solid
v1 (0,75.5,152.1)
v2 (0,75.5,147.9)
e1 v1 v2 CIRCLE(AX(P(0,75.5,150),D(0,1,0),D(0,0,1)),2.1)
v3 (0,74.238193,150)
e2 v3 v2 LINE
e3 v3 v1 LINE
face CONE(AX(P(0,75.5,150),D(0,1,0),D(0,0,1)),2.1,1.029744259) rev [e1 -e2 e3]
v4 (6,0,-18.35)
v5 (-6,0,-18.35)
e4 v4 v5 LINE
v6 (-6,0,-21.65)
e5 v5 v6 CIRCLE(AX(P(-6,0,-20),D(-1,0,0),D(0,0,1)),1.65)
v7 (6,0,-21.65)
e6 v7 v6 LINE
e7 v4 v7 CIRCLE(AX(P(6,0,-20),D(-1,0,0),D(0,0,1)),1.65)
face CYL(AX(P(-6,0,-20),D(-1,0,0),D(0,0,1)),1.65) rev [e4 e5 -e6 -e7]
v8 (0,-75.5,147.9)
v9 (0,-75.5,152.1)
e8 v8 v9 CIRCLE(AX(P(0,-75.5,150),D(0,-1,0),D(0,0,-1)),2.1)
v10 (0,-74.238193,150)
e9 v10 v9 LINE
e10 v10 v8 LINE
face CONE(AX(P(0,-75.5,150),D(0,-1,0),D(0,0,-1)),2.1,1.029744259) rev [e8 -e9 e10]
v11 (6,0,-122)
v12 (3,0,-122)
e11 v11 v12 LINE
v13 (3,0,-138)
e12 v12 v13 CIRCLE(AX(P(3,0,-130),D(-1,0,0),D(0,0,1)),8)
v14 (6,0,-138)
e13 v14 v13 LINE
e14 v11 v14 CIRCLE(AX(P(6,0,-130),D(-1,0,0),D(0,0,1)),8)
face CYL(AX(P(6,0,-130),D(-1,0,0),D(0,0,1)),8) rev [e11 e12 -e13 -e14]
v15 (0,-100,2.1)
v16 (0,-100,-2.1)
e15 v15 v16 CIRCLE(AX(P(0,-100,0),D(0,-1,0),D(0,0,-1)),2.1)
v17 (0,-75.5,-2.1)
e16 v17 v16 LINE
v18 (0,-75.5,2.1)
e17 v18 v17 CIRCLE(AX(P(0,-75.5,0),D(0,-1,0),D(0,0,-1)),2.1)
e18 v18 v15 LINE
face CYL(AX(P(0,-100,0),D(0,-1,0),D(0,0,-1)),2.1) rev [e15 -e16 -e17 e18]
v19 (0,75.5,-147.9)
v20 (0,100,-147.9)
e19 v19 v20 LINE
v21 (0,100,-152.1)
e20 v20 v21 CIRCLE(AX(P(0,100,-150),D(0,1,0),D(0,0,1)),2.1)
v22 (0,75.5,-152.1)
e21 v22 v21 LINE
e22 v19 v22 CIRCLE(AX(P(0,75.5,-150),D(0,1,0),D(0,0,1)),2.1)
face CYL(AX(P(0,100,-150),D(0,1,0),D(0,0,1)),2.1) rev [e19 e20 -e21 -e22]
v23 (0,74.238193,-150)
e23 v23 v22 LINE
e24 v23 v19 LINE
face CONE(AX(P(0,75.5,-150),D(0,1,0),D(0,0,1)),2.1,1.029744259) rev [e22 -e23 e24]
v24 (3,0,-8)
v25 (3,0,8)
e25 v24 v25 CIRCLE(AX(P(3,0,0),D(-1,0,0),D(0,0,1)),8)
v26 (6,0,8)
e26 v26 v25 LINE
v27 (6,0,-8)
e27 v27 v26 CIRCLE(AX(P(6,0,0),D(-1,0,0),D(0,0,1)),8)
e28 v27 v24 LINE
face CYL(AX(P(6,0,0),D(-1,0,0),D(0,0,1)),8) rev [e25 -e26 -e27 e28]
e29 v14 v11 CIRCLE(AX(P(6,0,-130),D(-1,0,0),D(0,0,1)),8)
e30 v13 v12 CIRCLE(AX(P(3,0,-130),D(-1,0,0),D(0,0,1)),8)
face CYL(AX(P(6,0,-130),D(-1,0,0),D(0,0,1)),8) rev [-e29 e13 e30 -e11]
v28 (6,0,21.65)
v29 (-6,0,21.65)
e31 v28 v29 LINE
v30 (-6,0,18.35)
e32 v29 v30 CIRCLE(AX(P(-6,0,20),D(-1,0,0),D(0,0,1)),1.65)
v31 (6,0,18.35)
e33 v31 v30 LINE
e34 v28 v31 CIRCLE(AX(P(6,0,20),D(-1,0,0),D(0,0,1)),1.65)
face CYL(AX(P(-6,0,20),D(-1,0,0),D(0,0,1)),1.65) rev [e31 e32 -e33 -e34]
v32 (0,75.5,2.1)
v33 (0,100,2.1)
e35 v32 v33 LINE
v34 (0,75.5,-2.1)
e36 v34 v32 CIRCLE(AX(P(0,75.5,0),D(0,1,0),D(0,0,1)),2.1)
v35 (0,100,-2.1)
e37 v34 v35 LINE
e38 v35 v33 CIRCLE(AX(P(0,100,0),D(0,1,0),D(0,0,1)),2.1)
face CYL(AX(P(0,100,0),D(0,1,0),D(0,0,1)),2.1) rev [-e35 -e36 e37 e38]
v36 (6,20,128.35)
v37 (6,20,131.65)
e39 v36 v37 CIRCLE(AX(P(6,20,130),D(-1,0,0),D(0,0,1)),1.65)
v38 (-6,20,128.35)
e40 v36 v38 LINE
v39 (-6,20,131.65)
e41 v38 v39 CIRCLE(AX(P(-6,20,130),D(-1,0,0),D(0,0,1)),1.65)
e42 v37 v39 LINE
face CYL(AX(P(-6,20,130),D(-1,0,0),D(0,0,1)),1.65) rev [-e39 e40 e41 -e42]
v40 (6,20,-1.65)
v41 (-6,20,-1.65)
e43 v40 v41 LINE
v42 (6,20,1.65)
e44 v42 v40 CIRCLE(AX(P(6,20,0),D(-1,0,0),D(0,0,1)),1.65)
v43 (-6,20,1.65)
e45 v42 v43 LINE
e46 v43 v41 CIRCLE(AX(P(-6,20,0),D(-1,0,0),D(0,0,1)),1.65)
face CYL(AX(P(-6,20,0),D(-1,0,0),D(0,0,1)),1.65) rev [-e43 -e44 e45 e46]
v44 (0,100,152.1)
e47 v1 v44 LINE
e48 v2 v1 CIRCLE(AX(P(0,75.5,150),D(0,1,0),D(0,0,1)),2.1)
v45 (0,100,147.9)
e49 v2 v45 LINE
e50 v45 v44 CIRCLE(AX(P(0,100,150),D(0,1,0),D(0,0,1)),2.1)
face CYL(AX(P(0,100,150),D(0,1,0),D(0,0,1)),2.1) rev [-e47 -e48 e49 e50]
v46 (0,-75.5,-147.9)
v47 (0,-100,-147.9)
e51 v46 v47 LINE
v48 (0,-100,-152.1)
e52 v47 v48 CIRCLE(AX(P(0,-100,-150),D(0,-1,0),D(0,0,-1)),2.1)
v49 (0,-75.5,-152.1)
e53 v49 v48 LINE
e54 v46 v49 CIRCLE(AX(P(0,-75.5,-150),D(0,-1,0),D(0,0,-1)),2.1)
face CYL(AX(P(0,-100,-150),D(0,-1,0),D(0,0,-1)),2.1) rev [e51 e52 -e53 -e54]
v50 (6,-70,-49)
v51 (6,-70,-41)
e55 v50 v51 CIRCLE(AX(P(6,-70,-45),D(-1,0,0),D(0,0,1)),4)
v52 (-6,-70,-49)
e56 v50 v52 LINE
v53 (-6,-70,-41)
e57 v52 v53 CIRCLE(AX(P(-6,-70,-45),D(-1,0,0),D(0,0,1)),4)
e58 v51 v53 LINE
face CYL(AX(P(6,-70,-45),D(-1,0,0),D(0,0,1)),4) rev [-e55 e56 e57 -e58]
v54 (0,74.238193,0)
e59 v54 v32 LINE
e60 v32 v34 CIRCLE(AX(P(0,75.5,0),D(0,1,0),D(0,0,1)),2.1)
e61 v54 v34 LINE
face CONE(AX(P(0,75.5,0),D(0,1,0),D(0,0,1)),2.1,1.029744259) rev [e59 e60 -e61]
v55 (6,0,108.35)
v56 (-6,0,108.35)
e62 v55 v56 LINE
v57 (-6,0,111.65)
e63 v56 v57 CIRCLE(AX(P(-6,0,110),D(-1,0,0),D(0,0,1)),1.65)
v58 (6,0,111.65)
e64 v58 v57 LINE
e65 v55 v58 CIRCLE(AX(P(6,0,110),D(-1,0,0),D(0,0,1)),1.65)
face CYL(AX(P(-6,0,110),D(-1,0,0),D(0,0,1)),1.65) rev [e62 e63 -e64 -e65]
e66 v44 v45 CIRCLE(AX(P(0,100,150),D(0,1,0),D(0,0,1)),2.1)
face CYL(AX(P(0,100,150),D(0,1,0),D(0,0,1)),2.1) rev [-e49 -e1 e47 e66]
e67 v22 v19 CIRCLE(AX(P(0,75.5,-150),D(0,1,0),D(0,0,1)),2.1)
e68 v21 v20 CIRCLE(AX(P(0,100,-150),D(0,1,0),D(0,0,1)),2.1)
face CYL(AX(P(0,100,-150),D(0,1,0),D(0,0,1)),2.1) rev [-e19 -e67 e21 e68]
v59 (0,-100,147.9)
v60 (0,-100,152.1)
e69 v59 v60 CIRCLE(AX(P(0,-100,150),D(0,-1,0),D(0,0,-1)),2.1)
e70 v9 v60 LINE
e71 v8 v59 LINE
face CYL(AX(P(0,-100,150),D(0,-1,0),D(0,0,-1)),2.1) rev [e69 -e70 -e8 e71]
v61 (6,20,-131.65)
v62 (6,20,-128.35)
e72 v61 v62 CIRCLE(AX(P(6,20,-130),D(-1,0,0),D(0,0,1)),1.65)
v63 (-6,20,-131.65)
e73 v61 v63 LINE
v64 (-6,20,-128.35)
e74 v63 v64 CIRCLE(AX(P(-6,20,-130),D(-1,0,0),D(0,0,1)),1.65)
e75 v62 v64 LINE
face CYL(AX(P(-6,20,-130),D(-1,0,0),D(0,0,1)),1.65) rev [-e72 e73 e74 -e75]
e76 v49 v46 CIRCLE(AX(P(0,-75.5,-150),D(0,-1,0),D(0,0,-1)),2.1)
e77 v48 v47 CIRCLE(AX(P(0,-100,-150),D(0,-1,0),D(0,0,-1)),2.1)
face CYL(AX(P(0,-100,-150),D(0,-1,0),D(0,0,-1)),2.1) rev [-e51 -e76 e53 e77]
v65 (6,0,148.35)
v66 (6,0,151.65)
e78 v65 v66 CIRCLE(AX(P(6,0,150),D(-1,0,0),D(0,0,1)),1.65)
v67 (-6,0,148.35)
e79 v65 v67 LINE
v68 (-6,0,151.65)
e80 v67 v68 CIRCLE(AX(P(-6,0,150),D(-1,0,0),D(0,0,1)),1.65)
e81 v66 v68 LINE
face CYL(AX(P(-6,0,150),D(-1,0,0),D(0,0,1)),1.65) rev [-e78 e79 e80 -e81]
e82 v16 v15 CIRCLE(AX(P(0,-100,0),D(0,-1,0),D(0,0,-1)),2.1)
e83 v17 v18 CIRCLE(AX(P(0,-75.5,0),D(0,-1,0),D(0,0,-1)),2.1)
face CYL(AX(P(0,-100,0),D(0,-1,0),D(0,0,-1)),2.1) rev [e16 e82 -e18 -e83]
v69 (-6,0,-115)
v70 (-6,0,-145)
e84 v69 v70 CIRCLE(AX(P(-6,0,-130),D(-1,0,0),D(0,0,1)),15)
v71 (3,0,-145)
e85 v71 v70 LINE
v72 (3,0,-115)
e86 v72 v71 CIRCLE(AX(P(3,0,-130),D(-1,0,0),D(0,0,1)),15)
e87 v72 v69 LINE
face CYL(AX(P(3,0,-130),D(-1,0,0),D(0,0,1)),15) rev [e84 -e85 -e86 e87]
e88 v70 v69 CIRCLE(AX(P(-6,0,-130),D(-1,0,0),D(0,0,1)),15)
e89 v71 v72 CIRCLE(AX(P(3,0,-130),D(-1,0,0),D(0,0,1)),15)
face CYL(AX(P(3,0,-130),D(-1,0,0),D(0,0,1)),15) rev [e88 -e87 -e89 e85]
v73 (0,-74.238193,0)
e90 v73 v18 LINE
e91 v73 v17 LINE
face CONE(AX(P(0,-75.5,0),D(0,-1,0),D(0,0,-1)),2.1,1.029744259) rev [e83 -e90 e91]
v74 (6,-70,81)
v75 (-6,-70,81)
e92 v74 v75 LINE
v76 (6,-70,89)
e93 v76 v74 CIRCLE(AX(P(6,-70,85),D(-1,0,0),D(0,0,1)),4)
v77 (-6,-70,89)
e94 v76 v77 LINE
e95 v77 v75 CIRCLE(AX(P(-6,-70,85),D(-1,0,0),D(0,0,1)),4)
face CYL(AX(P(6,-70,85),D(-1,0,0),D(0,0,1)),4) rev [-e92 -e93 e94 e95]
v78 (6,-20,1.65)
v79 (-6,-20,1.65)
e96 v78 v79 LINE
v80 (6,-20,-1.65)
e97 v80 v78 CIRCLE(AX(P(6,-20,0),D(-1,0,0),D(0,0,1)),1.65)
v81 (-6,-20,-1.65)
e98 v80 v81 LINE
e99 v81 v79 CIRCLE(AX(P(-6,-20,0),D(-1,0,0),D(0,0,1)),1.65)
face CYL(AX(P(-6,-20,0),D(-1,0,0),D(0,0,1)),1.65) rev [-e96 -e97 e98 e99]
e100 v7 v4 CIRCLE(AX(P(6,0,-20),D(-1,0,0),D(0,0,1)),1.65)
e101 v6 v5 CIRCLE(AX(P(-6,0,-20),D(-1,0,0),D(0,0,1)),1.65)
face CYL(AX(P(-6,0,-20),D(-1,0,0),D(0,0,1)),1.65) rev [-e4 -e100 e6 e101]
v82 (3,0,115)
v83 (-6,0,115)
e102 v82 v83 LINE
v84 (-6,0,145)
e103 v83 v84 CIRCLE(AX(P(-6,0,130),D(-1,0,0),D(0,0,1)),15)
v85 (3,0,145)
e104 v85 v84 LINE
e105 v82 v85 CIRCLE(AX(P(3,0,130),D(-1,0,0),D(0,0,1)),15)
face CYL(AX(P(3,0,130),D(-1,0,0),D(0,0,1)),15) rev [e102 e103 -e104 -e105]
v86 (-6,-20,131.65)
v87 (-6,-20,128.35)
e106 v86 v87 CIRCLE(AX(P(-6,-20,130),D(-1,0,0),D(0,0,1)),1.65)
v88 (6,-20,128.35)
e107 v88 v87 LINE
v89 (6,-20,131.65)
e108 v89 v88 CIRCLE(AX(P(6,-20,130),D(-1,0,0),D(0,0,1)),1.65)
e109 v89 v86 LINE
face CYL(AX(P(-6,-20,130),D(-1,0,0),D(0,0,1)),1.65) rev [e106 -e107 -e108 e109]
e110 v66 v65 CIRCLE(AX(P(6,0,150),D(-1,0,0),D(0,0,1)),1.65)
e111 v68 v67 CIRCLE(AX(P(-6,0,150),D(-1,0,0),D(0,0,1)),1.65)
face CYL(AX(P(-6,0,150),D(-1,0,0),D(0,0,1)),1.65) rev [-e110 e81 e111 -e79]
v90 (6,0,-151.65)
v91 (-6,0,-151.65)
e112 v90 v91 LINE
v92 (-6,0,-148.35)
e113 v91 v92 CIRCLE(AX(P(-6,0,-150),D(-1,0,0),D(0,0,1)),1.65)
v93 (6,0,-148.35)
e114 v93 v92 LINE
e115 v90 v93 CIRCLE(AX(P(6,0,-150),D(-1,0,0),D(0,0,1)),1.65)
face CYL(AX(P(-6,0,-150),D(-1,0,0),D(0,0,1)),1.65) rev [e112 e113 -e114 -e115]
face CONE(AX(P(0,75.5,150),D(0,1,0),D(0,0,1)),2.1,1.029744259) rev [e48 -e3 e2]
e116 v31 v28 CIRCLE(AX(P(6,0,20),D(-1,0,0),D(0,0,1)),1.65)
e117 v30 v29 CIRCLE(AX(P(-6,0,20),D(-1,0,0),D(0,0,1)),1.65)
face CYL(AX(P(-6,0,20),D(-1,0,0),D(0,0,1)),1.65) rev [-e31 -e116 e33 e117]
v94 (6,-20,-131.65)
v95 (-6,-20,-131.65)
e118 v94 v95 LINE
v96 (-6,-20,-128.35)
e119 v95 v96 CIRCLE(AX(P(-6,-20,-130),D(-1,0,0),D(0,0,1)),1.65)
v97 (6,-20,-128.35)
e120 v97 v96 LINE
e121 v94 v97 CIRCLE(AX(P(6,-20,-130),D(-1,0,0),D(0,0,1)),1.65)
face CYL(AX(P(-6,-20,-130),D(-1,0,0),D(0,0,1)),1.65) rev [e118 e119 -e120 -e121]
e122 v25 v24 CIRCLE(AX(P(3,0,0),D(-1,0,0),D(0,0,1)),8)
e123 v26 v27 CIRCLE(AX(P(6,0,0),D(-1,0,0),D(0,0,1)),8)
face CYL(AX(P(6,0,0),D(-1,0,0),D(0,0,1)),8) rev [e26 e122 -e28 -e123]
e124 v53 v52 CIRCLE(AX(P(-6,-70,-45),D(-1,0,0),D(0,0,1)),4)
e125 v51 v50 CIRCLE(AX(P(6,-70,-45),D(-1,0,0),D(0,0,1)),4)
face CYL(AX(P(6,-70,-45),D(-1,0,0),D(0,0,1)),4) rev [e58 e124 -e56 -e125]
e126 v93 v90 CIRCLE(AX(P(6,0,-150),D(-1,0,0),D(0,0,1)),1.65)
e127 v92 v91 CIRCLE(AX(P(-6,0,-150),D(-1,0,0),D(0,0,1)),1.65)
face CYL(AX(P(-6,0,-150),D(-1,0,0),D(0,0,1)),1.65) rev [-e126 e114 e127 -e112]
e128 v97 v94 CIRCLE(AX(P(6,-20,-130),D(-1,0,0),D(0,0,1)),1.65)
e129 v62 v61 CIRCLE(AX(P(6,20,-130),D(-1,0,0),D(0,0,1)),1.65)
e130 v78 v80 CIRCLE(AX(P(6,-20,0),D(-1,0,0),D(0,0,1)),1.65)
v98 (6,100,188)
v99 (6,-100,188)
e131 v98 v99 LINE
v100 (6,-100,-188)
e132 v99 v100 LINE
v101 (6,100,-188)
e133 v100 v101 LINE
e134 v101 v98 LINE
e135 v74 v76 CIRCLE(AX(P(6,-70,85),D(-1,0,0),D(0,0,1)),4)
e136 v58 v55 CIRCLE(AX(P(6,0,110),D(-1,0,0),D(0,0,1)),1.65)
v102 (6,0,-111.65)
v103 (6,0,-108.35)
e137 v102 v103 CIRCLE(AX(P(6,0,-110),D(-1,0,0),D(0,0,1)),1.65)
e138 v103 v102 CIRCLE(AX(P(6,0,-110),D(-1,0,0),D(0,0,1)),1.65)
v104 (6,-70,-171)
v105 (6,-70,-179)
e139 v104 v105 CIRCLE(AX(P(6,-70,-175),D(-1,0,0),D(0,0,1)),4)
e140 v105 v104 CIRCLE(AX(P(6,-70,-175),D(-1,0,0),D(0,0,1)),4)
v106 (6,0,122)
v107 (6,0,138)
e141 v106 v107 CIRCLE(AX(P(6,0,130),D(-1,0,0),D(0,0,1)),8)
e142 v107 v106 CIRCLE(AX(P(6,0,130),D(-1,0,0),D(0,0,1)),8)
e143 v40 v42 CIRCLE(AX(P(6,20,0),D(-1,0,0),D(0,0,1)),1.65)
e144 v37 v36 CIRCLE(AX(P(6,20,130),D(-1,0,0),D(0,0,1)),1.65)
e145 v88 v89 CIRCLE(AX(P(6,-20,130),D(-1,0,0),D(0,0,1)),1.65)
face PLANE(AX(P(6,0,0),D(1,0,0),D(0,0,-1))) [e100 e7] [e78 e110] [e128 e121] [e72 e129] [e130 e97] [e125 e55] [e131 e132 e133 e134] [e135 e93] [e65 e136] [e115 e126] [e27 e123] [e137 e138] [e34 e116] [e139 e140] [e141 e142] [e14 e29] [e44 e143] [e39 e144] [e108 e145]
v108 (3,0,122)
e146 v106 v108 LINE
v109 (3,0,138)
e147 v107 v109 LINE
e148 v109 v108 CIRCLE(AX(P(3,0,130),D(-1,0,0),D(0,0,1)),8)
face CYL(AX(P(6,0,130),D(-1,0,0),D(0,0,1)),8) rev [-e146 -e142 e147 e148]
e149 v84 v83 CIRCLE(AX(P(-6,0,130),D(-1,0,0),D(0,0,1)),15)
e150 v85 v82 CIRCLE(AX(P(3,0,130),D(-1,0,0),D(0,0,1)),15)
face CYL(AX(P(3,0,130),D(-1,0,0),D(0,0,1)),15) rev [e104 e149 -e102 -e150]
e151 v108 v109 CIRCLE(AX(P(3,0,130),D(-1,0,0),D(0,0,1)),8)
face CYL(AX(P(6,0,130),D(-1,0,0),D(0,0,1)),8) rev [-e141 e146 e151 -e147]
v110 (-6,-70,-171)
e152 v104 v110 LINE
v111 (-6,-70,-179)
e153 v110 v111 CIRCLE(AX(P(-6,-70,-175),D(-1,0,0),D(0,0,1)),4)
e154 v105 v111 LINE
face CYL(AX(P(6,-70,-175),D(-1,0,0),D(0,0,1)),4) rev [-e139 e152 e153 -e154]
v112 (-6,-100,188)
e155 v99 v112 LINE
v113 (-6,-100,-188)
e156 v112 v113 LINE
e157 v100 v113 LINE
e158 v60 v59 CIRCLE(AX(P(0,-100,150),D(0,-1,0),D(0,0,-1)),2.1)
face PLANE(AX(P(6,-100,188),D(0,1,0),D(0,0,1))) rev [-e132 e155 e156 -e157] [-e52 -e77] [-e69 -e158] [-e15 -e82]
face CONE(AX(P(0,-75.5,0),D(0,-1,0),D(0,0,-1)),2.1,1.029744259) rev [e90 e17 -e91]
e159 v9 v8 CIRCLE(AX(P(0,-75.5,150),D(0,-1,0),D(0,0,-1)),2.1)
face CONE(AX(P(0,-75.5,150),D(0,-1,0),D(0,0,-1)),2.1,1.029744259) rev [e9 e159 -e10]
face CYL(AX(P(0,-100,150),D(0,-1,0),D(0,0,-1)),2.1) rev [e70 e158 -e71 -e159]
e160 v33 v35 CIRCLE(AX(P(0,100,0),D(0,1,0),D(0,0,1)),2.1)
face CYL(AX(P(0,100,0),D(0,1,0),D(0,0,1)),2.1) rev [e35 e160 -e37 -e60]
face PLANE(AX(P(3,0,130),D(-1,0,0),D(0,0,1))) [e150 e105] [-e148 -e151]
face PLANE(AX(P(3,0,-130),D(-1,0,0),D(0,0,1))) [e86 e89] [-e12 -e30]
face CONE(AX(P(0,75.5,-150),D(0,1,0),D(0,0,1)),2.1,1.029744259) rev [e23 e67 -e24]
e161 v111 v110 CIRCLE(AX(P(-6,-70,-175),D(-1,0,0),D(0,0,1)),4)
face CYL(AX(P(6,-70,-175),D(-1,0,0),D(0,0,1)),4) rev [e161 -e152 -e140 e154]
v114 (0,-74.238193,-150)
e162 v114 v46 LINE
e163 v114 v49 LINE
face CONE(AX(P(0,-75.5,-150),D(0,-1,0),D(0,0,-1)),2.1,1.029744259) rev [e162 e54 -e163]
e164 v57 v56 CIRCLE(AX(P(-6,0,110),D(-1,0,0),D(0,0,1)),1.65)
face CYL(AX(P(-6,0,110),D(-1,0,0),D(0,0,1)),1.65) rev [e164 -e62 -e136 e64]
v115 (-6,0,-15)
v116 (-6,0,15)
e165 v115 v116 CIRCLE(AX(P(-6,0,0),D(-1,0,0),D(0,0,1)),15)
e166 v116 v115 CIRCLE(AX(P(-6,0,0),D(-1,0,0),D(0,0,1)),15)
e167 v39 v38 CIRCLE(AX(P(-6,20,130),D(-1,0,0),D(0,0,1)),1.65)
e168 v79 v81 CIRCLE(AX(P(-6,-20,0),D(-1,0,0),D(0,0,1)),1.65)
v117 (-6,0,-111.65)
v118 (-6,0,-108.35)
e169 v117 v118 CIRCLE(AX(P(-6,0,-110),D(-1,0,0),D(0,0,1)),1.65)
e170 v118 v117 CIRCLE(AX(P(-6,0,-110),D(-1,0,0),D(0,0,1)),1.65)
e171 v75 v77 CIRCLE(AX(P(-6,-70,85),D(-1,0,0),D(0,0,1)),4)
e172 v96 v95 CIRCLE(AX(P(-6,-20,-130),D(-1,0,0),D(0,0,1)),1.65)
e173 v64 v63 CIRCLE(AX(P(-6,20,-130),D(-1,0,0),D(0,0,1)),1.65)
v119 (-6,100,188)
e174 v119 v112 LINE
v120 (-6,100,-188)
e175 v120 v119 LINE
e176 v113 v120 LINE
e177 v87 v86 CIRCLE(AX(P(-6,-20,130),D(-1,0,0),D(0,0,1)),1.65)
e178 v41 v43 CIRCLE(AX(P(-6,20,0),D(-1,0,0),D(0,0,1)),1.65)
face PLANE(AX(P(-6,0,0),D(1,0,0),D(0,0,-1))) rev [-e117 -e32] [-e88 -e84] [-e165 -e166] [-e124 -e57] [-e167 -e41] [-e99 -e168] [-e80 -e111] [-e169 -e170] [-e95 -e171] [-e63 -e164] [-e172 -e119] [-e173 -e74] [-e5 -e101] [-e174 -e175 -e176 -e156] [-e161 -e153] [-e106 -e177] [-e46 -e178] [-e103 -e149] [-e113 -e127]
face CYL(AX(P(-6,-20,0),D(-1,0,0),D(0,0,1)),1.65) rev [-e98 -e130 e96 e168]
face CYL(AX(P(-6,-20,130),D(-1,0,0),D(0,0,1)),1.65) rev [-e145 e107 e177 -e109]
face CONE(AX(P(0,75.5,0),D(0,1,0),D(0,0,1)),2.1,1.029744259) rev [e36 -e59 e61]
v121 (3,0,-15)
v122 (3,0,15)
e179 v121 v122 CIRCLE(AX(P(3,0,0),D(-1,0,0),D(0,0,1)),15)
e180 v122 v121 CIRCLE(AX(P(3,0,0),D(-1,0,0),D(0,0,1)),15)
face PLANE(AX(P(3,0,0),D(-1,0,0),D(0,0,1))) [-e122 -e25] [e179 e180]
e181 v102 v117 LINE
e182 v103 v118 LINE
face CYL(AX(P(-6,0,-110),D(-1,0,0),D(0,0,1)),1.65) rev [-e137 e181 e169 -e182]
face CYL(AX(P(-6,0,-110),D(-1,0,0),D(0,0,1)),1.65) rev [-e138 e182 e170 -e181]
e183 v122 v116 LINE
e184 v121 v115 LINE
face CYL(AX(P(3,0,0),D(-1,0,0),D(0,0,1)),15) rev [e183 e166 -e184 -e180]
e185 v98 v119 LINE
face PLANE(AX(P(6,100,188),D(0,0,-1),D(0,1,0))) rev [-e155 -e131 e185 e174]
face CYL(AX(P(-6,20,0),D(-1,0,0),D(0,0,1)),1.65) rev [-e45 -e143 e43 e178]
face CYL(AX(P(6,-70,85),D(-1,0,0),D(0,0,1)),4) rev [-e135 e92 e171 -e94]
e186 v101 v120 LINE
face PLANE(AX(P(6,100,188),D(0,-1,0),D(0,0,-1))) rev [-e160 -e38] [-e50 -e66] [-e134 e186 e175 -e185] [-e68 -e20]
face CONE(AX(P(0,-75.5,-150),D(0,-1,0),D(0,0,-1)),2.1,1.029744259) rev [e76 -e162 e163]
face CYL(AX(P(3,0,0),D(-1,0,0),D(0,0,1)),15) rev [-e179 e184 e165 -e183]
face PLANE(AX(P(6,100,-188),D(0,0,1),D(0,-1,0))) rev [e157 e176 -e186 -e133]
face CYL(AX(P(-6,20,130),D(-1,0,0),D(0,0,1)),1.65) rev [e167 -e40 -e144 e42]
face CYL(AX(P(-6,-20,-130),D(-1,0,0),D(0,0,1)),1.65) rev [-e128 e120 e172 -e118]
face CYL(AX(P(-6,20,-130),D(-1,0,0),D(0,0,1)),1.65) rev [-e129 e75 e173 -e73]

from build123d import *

# Parameters (mm, degrees)
SKETCH1_W                  = 376
SKETCH1_H                  = 200
BOSS_EXTRUDE1_DEPTH        = 6
M5_TAPPED_HOLE1_AT_2_COUNT = 2
M5_TAPPED_HOLE1_AT_2_PITCH = 300
M5_TAPPED_HOLE1_AT_3_COUNT = 2
M5_TAPPED_HOLE1_AT_3_PITCH = 150
SKETCH4_R                  = 15
CUT_EXTRUDE1_DEPTH         = 9
SKETCH6_R                  = 8
CUT_EXTRUDE2_DEPTH         = 214.279159788
M4_TAPPED_HOLE1_D          = 3.3
SKETCH9_R                  = 4
CUT_EXTRUDE3_DEPTH         = 214.279159788


with BuildPart() as part:
    # Sketch1 → Boss-Extrude1 (new, symmetric)
    with BuildSketch(Plane(origin=(0, 0, 0), x_dir=(0, 0, -1), z_dir=(1, 0, 0))):
        Rectangle(SKETCH1_W, SKETCH1_H)
    extrude(amount=BOSS_EXTRUDE1_DEPTH, both=True)

    # Sketch3 → M5 Tapped Hole1 (revolve, cut)
    with BuildSketch(Plane(origin=(0, 100, -150), x_dir=(0, 0, 1), z_dir=(1, 0, 0))):
        Polygon((0, 0), (0, 25.7618073), (2.1, 24.5), (2.1, 0), align=None)
    m5_tapped_hole1 = revolve(axis=Axis((0, 106.35, -150), (0, -1, 0)), mode=Mode.SUBTRACT)

    # M5 Tapped Hole1 at 2: M5 Tapped Hole1 ×2
    with Locations(*[(0, 0, i * M5_TAPPED_HOLE1_AT_2_PITCH) for i in range(1, M5_TAPPED_HOLE1_AT_2_COUNT)]):
        add(m5_tapped_hole1, mode=Mode.SUBTRACT)

    # M5 Tapped Hole1 at 3: M5 Tapped Hole1 ×2
    with Locations(*[(0, 0, i * M5_TAPPED_HOLE1_AT_3_PITCH) for i in range(1, M5_TAPPED_HOLE1_AT_3_COUNT)]):
        add(m5_tapped_hole1, mode=Mode.SUBTRACT)

    # Mirror1: M5 Tapped Hole1 across plane
    add(m5_tapped_hole1.mirror(Plane.ZX), mode=Mode.SUBTRACT)

    # Mirror1 copy 1 sketch → Mirror1 copy 1 (revolve, cut)
    with BuildSketch(Plane(origin=(0, -100, 150), x_dir=(0, 0, 1), z_dir=(1, 0, 0))):
        Polygon((0, 0), (0, -25.7618073), (2.1, -24.5), (2.1, 0), align=None)
    revolve(axis=Axis((0, -106.35, 150), (0, -1, 0)), mode=Mode.SUBTRACT)

    # Mirror1 copy 2 sketch → Mirror1 copy 2 (revolve, cut)
    with BuildSketch(Plane(origin=(0, -100, 0), x_dir=(0, 0, 1), z_dir=(1, 0, 0))):
        Polygon((0, 0), (0, -25.7618073), (2.1, -24.5), (2.1, 0), align=None)
    revolve(axis=Axis((0, -106.35, 0), (0, -1, 0)), mode=Mode.SUBTRACT)

    # Sketch4 → Cut-Extrude1 (cut)
    with BuildSketch(Plane.ZY.offset(6)):
        with Locations((-130, 0)):
            Circle(SKETCH4_R)
        Circle(SKETCH4_R)
        with Locations((130, 0)):
            Circle(SKETCH4_R)
    extrude(amount=-CUT_EXTRUDE1_DEPTH, mode=Mode.SUBTRACT)

    # Sketch6 → Cut-Extrude2 (cut, through all)
    with BuildSketch(Plane.ZY.offset(6)):
        with Locations((-130, 0)):
            Circle(SKETCH6_R)
        Circle(SKETCH6_R)
        with Locations((130, 0)):
            Circle(SKETCH6_R)
    extrude(amount=-CUT_EXTRUDE2_DEPTH, mode=Mode.SUBTRACT)

    # M4 Tapped Hole1 (through all)
    with Locations(Plane.ZY.offset(6)):
        with Locations((130, -20), (-150, 0), (-130, 20), (-110, 0), (-130, -20), (-20, 0), (0, 20), (20, 0), (0, -20), (110, 0), (130, 20), (150, 0)):
            Hole(M4_TAPPED_HOLE1_D / 2)

    # Sketch9 → Cut-Extrude3 (cut, through all)
    with BuildSketch(Plane.ZY.offset(6)):
        with Locations((-175, -70)):
            Circle(SKETCH9_R)
        with Locations((-45, -70)):
            Circle(SKETCH9_R)
        with Locations((85, -70)):
            Circle(SKETCH9_R)
    extrude(amount=-CUT_EXTRUDE3_DEPTH, mode=Mode.SUBTRACT)


solid = part.part
